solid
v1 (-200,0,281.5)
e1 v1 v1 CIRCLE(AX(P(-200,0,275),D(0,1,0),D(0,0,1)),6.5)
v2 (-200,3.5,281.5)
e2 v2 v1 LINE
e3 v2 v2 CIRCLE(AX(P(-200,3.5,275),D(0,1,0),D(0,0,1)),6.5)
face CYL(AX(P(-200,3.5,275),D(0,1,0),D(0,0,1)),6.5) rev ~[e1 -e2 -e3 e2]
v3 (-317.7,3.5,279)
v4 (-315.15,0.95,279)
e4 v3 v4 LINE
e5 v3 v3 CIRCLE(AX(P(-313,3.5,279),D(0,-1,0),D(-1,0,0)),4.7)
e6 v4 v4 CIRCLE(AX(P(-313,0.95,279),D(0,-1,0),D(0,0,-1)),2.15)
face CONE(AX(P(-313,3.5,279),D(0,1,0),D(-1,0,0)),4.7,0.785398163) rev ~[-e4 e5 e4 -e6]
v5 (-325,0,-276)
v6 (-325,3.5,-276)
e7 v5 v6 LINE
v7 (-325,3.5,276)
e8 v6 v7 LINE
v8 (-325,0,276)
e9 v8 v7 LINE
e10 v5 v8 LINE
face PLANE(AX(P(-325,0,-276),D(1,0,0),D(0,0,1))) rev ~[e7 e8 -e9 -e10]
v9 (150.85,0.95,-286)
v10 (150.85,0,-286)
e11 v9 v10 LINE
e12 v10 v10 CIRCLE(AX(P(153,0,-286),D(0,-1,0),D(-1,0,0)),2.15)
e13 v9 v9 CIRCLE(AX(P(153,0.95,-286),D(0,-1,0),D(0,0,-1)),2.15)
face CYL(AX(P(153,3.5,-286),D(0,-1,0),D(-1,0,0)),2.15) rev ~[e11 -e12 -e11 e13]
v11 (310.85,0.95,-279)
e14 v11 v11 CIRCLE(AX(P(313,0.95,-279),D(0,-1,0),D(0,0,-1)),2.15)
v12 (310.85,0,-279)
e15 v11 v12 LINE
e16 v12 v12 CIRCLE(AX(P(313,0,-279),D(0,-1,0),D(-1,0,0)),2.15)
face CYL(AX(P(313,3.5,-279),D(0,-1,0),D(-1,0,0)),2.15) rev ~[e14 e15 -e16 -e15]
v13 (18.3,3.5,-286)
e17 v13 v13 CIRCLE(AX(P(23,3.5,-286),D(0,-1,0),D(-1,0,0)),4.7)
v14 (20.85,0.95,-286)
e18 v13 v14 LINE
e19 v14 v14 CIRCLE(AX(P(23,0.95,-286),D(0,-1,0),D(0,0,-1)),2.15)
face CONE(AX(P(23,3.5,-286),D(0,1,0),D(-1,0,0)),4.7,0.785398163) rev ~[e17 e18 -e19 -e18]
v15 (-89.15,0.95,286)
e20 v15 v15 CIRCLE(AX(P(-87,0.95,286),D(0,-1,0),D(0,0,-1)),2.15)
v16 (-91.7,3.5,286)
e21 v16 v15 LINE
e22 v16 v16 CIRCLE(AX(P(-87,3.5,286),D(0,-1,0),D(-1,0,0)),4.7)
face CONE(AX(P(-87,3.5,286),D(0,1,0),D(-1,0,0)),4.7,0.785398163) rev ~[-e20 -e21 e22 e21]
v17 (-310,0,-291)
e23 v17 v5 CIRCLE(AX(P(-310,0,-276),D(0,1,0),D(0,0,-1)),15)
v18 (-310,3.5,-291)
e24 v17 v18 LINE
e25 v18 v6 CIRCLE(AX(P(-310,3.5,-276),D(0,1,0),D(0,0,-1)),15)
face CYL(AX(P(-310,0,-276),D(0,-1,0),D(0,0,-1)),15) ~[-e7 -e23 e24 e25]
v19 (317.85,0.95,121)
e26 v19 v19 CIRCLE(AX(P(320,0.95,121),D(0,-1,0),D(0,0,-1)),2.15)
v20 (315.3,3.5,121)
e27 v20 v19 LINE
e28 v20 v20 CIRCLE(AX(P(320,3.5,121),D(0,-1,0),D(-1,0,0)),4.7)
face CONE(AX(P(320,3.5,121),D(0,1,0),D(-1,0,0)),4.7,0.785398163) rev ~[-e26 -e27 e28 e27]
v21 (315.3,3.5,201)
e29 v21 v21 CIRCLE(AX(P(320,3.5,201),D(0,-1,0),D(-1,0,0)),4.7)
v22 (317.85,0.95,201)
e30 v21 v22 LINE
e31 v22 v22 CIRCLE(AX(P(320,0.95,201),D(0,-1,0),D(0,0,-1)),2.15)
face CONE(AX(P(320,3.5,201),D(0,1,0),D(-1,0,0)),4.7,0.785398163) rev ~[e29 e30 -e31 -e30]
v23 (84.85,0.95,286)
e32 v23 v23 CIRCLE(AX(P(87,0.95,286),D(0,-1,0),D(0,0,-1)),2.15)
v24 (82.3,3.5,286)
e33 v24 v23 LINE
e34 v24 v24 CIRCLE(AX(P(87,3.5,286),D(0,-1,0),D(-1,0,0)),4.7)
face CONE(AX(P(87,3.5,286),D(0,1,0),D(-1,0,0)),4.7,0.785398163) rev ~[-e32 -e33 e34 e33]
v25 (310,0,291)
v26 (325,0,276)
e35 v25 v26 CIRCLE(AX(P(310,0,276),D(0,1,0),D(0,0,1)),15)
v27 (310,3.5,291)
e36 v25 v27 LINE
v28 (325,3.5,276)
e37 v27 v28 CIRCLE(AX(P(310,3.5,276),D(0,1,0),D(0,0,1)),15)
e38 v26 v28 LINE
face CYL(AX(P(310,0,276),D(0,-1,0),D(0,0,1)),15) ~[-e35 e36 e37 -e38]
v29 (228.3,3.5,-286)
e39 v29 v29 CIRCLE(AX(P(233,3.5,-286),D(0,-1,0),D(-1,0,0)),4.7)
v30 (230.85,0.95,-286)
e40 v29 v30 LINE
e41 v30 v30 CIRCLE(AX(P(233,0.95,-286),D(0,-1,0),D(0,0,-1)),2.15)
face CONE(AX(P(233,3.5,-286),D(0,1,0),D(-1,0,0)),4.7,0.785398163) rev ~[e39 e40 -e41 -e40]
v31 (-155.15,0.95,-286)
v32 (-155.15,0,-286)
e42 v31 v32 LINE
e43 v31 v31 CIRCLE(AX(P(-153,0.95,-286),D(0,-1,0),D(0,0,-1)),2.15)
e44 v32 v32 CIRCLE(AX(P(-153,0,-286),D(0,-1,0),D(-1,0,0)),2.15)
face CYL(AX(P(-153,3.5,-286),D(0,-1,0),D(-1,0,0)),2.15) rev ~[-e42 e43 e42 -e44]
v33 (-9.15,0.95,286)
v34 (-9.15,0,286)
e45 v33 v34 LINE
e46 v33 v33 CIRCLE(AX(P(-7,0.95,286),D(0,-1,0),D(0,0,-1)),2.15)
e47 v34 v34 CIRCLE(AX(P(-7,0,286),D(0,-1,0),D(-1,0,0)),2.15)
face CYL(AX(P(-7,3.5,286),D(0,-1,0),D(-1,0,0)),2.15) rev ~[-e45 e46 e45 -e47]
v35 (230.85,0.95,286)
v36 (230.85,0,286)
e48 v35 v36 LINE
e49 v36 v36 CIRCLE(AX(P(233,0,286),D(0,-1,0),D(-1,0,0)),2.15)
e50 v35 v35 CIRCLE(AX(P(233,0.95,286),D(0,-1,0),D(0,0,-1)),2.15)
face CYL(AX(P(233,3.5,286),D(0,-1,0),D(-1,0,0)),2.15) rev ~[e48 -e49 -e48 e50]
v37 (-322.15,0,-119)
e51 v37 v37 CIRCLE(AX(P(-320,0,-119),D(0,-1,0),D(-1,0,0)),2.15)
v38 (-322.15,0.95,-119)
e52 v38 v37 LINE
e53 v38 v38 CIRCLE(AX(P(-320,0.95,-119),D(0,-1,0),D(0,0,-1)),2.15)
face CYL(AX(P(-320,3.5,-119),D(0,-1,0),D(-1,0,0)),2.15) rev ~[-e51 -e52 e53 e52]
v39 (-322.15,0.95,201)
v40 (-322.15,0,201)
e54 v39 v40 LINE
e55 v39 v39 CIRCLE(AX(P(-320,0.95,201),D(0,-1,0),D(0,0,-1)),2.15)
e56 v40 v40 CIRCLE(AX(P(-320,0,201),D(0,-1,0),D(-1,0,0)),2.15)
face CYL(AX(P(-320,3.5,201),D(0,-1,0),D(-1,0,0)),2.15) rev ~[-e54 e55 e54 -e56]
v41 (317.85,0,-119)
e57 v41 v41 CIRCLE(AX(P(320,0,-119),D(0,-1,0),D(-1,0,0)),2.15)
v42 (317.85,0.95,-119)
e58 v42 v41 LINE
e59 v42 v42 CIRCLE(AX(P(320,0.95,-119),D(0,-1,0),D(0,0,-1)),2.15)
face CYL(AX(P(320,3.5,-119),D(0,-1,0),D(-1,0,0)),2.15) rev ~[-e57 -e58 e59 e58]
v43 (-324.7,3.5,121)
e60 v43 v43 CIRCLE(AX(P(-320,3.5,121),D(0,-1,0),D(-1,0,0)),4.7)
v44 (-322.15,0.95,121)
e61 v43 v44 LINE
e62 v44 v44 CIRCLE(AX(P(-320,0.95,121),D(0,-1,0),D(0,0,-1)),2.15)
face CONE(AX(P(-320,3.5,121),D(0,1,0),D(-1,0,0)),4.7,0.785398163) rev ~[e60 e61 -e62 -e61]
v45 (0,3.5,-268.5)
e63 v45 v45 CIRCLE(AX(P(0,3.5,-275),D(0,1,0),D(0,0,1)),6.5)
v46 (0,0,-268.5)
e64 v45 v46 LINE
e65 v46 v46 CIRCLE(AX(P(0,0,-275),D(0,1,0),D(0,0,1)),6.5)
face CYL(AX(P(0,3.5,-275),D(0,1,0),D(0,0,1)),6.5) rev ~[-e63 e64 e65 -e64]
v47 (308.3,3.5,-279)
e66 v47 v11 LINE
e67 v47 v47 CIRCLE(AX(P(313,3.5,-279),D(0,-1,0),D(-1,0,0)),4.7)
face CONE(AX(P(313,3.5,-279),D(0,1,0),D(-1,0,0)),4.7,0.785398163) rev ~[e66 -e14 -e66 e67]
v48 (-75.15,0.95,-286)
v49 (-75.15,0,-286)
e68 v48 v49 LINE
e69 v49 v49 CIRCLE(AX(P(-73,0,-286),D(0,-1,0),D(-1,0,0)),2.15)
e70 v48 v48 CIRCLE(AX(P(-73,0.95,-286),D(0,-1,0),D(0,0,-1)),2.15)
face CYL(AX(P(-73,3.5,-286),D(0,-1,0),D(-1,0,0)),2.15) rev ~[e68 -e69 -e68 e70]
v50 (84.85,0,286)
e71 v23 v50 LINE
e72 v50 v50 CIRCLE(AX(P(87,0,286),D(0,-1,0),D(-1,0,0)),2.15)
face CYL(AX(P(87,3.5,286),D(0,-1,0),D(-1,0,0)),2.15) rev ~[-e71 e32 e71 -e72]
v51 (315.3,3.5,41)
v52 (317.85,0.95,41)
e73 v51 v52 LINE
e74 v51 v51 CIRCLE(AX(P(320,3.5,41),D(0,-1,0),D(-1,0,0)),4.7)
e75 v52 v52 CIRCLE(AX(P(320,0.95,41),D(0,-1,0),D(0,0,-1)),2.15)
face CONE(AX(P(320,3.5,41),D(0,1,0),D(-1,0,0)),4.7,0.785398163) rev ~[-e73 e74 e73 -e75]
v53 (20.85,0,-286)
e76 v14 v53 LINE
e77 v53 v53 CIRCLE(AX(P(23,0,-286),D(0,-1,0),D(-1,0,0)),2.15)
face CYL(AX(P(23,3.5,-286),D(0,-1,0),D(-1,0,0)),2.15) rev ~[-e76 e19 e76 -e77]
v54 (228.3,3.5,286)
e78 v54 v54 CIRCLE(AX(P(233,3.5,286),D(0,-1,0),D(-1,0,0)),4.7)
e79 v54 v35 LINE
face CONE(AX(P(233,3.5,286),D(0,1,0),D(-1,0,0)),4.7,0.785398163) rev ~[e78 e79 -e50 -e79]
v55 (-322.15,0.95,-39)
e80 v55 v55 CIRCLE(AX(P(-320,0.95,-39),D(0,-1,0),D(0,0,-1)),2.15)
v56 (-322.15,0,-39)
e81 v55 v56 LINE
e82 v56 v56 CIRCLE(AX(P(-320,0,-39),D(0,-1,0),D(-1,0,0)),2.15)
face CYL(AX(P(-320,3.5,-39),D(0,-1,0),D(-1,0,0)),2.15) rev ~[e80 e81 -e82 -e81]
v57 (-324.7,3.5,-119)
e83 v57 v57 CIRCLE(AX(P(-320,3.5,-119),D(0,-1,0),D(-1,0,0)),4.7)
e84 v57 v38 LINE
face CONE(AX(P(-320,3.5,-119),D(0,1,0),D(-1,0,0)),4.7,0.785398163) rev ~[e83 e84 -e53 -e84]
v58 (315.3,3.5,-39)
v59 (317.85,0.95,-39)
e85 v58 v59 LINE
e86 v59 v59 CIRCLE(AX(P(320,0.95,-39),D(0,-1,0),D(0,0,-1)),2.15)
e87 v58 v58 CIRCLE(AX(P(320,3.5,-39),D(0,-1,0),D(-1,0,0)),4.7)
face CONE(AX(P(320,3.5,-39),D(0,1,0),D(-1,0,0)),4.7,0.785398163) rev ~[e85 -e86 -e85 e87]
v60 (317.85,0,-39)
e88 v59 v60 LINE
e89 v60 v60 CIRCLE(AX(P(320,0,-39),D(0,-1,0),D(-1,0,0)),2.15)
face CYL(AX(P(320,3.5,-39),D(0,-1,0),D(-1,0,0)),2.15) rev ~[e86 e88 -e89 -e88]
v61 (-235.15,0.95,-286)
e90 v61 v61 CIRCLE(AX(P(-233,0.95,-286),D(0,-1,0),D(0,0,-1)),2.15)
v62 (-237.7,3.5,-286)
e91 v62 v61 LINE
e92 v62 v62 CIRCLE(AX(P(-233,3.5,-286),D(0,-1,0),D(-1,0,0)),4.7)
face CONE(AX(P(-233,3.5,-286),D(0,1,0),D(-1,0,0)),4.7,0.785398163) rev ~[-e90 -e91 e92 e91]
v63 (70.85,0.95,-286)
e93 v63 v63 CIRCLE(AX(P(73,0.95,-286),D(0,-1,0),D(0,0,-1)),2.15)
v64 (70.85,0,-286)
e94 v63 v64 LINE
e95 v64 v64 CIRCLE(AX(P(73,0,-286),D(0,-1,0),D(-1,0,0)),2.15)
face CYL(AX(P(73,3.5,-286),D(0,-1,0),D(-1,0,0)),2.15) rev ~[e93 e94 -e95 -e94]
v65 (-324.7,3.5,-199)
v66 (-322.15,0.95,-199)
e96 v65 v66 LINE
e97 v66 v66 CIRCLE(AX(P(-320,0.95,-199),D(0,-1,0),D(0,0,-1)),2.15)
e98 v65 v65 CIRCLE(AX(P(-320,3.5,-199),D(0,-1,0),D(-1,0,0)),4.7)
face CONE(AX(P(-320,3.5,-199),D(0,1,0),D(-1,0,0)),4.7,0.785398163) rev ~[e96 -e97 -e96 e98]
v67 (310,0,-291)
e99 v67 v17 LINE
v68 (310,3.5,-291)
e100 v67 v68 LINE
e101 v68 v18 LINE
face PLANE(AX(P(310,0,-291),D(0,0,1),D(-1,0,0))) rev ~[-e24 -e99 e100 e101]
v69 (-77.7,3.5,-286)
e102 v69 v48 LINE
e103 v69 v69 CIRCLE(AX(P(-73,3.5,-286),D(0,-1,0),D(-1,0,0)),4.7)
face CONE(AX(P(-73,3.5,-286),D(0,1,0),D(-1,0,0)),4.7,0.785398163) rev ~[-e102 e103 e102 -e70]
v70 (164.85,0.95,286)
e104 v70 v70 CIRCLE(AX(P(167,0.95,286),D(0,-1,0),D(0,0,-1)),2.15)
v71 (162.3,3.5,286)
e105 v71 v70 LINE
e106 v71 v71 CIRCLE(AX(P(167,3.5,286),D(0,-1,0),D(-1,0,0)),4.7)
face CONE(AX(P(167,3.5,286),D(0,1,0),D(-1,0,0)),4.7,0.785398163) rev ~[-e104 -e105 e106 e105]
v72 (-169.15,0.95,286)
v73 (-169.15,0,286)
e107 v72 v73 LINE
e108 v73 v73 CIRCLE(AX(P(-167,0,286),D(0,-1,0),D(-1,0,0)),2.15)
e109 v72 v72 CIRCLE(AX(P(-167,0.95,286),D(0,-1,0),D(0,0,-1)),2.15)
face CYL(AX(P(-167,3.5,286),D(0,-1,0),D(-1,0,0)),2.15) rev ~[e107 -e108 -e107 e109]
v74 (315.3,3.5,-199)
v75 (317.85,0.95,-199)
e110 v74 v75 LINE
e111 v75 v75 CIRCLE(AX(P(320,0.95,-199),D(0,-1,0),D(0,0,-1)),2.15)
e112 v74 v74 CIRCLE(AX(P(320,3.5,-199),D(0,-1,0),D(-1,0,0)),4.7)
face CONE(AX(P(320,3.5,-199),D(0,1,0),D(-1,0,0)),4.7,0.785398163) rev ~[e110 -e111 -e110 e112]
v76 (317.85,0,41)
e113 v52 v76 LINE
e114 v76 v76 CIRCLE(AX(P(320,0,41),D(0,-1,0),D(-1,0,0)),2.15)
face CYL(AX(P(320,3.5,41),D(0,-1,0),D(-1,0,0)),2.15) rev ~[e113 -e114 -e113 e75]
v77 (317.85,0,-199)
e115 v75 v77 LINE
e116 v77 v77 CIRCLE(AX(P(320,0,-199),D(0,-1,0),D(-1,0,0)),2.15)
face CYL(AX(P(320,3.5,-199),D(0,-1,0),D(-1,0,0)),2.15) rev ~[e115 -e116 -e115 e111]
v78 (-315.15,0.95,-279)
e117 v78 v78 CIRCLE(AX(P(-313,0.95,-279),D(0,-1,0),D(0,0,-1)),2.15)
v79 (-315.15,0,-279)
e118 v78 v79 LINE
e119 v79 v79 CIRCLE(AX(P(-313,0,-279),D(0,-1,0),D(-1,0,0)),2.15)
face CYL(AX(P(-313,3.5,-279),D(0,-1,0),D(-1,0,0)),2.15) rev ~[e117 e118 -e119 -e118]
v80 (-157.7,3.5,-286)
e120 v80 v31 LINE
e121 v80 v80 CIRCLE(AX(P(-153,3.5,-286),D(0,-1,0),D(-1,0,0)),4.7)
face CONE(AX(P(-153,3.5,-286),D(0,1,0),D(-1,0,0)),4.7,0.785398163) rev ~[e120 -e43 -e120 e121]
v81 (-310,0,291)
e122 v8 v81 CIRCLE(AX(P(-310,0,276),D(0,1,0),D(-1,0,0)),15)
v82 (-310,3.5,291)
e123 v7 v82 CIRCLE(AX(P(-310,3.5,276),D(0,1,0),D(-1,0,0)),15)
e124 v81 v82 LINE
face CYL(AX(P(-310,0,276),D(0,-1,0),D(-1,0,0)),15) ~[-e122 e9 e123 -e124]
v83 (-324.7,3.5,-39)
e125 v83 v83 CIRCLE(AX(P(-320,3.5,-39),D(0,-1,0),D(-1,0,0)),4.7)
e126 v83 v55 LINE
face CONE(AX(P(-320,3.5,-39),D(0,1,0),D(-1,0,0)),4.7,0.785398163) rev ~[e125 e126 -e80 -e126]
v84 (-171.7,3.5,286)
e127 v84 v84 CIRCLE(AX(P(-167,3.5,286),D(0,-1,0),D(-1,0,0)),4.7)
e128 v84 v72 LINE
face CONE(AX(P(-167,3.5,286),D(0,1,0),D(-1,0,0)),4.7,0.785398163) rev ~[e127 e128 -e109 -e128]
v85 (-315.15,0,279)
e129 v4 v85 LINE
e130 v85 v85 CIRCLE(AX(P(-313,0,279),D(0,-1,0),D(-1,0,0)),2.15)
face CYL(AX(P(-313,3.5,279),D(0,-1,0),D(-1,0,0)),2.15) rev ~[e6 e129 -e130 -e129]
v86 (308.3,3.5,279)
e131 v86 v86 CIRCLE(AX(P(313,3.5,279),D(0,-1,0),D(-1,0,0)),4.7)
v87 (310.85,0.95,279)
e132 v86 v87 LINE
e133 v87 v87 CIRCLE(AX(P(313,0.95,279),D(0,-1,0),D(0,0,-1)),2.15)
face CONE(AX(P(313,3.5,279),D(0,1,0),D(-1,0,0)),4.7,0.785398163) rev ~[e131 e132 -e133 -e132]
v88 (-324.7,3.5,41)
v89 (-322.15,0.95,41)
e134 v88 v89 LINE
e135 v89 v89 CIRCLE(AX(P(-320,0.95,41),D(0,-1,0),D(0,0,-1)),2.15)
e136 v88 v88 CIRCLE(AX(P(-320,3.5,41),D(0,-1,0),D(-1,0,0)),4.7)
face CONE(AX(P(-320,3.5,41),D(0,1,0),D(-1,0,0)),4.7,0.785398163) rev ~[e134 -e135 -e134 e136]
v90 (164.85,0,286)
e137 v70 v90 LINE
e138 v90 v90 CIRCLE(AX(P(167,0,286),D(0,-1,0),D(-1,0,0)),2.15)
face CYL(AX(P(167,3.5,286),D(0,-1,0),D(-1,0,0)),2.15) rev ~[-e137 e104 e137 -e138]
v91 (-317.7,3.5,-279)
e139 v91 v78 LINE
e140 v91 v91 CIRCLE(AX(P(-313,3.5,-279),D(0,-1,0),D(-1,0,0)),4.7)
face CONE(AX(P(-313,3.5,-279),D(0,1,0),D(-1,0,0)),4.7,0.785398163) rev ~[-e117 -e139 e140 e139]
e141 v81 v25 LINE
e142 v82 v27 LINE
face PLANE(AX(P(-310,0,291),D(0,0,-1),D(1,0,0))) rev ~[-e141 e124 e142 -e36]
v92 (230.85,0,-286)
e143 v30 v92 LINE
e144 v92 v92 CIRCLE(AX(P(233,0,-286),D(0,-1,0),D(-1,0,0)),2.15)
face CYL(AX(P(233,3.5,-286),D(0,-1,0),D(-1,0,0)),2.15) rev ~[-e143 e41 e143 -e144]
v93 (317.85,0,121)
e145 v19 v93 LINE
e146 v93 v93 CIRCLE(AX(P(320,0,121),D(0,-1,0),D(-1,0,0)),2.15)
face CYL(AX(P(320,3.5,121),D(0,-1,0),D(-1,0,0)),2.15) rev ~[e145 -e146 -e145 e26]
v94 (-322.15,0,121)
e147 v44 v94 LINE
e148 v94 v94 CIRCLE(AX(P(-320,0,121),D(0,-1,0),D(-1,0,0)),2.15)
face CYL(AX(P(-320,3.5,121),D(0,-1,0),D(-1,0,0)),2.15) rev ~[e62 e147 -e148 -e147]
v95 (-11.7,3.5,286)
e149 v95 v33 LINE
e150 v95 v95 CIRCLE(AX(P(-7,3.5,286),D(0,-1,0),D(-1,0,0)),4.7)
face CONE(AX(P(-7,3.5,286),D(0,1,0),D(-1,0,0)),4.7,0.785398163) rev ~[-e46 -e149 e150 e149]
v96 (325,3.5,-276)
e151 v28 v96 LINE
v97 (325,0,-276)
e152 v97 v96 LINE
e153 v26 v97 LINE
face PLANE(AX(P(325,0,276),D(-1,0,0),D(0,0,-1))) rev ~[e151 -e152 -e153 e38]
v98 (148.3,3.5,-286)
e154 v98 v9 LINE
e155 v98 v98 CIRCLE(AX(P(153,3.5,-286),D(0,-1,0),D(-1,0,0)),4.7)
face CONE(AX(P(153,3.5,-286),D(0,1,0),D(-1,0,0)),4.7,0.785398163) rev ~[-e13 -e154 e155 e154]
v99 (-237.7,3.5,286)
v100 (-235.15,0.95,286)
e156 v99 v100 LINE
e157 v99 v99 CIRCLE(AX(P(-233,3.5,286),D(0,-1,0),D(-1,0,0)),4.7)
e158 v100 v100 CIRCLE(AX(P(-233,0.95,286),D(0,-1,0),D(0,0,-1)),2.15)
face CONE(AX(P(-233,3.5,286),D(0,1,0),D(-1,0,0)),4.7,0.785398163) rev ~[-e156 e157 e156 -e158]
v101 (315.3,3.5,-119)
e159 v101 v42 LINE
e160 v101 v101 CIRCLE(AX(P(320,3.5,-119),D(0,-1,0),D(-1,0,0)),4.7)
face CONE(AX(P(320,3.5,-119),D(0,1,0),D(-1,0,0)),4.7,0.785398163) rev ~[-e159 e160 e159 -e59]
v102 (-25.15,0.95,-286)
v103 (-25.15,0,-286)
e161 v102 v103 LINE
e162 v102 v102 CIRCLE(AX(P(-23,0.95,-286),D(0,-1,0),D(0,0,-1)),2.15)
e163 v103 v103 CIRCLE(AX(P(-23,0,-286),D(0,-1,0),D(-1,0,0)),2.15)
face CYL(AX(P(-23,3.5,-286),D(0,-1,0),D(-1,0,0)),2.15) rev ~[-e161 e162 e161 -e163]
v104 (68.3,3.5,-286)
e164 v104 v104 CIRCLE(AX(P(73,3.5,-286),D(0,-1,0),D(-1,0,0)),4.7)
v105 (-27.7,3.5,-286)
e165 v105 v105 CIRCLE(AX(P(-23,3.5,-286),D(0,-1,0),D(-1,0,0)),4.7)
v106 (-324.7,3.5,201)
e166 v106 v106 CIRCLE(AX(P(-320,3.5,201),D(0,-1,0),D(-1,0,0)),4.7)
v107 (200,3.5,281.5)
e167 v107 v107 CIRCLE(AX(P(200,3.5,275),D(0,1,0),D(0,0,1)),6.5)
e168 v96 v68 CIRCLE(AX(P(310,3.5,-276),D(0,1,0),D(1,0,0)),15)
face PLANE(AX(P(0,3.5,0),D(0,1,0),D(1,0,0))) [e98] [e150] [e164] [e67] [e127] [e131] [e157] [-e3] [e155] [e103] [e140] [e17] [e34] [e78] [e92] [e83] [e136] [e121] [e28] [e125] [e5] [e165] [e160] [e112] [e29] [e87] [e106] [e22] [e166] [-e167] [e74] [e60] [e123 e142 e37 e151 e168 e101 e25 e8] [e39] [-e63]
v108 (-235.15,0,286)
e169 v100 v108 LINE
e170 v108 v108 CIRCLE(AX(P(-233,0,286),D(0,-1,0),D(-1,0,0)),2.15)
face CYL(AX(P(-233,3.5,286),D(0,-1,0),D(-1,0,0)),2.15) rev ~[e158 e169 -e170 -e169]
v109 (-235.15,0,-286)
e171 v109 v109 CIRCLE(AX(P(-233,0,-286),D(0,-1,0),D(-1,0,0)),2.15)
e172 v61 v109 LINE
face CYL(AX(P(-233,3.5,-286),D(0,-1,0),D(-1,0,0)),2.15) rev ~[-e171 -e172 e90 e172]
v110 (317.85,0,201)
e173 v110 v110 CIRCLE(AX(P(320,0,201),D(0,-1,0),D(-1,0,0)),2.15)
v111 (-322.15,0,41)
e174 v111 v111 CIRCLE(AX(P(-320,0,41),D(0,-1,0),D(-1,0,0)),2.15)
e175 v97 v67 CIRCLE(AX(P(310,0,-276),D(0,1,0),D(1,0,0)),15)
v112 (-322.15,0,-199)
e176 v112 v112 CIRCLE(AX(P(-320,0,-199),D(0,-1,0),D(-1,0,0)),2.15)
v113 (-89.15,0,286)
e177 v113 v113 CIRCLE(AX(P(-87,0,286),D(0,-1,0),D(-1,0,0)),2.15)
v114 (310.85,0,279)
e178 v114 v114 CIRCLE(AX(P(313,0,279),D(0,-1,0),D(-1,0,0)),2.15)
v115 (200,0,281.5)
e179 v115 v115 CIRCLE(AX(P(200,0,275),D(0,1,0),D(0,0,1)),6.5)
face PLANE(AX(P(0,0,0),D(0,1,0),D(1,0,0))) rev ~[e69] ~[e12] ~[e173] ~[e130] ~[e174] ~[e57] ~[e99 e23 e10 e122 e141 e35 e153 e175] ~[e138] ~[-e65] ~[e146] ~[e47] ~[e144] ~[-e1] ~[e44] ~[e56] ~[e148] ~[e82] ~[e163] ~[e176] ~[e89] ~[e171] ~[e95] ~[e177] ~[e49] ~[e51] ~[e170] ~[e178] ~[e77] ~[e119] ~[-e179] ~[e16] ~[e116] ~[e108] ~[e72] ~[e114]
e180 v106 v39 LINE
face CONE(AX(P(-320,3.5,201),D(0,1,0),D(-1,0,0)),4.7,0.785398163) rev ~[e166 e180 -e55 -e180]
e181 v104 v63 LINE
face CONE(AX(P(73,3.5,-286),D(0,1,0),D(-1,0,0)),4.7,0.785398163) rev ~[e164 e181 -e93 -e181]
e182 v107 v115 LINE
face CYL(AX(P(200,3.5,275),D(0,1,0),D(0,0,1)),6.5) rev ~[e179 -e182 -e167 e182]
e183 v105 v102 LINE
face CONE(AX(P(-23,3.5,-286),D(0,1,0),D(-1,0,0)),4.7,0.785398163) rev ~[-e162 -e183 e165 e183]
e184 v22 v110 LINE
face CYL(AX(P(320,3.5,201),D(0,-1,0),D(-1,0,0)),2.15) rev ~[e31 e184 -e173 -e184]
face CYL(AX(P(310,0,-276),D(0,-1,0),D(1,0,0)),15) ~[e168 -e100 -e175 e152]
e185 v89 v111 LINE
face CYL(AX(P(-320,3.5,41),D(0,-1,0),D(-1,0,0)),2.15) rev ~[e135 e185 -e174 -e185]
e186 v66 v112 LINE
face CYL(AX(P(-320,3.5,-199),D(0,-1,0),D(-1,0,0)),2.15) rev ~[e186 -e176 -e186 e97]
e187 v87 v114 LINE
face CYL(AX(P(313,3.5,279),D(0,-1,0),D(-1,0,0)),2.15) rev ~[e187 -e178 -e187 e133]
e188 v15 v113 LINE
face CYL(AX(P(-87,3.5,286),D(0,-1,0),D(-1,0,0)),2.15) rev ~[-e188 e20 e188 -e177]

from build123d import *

# Parameters (mm, degrees)
BOSS_EXTRUDE1_DEPTH                             = 3.5
SKETCH2_R                                       = 6.5
CUT_EXTRUDE1_DEPTH                              = 437.254799401
CSK_FOR_M4_FLAT_HEAD_MACHINE_SCREW1_D           = 4.3
CSK_FOR_M4_FLAT_HEAD_MACHINE_SCREW1_DEPTH       = 7.5
CSK_FOR_M4_FLAT_HEAD_MACHINE_SCREW1_CSINK_D     = 9.4
CSK_FOR_M4_FLAT_HEAD_MACHINE_SCREW1_CSINK_ANGLE = 90
CSK_FOR_M4_FLAT_HEAD_MACHINE_SCREW1_TIP         = 1.291850331


with BuildPart() as part:
    # Sketch1 → Boss-Extrude1 (new body)
    with BuildSketch(Plane(origin=(0, 0, 0), x_dir=(1, 0, 0), z_dir=(0, 1, 0))):
        with BuildLine():
            Line((-310, -291), (310, -291))
            ThreePointArc((310, -291), (320.606601718, -286.606601718), (325, -276))
            Line((325, -276), (325, 276))
            ThreePointArc((325, 276), (320.606601718, 286.606601718), (310, 291))
            Line((310, 291), (-310, 291))
            ThreePointArc((-310, 291), (-320.606601718, 286.606601718), (-325, 276))
            Line((-325, 276), (-325, -276))
            ThreePointArc((-325, -276), (-320.606601718, -286.606601718), (-310, -291))
        make_face()
    extrude(amount=BOSS_EXTRUDE1_DEPTH)

    # Sketch2 → Cut-Extrude1 (cut, through all)
    with BuildSketch(Plane(origin=(0, 3.5, 0), x_dir=(1, 0, 0), z_dir=(0, 1, 0))):
        with Locations(Location((0, 275, 0), (0, 0, 270))):
            Circle(SKETCH2_R)
        with Locations(Location((200, -275, 0), (0, 0, 270))):
            Circle(SKETCH2_R)
        with Locations(Location((-200, -275, 0), (0, 0, 270))):
            Circle(SKETCH2_R)
    extrude(amount=-CUT_EXTRUDE1_DEPTH, mode=Mode.SUBTRACT)

    # CSK for M4 Flat Head Machine Screw1
    with Locations(Plane(origin=(0, 3.5, 0), x_dir=(1, 0, 0), z_dir=(0, 1, 0))):
        with Locations((-233, 286), (-313, 279), (-153, 286), (-73, 286), (-23, 286), (73, 286), (153, 286), (313, 279), (-320, 199), (-320, 119), (-320, 39), (-320, -41), (-320, -121), (-320, -201), (-313, -279), (-233, -286), (-167, -286), (-87, -286), (-7, -286), (87, -286), (167, -286), (313, -279), (320, -201), (320, -121), (320, -41), (320, 39), (320, 119), (320, 199), (233, 286), (23, 286), (233, -286)):
            CounterSinkHole(CSK_FOR_M4_FLAT_HEAD_MACHINE_SCREW1_D / 2, CSK_FOR_M4_FLAT_HEAD_MACHINE_SCREW1_CSINK_D / 2, depth=CSK_FOR_M4_FLAT_HEAD_MACHINE_SCREW1_DEPTH, counter_sink_angle=CSK_FOR_M4_FLAT_HEAD_MACHINE_SCREW1_CSINK_ANGLE)
            with Locations((0, 0, -(CSK_FOR_M4_FLAT_HEAD_MACHINE_SCREW1_DEPTH + CSK_FOR_M4_FLAT_HEAD_MACHINE_SCREW1_TIP / 2))):  # 118° drill point
                Cone(0, CSK_FOR_M4_FLAT_HEAD_MACHINE_SCREW1_D / 2, CSK_FOR_M4_FLAT_HEAD_MACHINE_SCREW1_TIP, mode=Mode.SUBTRACT)


solid = part.part
